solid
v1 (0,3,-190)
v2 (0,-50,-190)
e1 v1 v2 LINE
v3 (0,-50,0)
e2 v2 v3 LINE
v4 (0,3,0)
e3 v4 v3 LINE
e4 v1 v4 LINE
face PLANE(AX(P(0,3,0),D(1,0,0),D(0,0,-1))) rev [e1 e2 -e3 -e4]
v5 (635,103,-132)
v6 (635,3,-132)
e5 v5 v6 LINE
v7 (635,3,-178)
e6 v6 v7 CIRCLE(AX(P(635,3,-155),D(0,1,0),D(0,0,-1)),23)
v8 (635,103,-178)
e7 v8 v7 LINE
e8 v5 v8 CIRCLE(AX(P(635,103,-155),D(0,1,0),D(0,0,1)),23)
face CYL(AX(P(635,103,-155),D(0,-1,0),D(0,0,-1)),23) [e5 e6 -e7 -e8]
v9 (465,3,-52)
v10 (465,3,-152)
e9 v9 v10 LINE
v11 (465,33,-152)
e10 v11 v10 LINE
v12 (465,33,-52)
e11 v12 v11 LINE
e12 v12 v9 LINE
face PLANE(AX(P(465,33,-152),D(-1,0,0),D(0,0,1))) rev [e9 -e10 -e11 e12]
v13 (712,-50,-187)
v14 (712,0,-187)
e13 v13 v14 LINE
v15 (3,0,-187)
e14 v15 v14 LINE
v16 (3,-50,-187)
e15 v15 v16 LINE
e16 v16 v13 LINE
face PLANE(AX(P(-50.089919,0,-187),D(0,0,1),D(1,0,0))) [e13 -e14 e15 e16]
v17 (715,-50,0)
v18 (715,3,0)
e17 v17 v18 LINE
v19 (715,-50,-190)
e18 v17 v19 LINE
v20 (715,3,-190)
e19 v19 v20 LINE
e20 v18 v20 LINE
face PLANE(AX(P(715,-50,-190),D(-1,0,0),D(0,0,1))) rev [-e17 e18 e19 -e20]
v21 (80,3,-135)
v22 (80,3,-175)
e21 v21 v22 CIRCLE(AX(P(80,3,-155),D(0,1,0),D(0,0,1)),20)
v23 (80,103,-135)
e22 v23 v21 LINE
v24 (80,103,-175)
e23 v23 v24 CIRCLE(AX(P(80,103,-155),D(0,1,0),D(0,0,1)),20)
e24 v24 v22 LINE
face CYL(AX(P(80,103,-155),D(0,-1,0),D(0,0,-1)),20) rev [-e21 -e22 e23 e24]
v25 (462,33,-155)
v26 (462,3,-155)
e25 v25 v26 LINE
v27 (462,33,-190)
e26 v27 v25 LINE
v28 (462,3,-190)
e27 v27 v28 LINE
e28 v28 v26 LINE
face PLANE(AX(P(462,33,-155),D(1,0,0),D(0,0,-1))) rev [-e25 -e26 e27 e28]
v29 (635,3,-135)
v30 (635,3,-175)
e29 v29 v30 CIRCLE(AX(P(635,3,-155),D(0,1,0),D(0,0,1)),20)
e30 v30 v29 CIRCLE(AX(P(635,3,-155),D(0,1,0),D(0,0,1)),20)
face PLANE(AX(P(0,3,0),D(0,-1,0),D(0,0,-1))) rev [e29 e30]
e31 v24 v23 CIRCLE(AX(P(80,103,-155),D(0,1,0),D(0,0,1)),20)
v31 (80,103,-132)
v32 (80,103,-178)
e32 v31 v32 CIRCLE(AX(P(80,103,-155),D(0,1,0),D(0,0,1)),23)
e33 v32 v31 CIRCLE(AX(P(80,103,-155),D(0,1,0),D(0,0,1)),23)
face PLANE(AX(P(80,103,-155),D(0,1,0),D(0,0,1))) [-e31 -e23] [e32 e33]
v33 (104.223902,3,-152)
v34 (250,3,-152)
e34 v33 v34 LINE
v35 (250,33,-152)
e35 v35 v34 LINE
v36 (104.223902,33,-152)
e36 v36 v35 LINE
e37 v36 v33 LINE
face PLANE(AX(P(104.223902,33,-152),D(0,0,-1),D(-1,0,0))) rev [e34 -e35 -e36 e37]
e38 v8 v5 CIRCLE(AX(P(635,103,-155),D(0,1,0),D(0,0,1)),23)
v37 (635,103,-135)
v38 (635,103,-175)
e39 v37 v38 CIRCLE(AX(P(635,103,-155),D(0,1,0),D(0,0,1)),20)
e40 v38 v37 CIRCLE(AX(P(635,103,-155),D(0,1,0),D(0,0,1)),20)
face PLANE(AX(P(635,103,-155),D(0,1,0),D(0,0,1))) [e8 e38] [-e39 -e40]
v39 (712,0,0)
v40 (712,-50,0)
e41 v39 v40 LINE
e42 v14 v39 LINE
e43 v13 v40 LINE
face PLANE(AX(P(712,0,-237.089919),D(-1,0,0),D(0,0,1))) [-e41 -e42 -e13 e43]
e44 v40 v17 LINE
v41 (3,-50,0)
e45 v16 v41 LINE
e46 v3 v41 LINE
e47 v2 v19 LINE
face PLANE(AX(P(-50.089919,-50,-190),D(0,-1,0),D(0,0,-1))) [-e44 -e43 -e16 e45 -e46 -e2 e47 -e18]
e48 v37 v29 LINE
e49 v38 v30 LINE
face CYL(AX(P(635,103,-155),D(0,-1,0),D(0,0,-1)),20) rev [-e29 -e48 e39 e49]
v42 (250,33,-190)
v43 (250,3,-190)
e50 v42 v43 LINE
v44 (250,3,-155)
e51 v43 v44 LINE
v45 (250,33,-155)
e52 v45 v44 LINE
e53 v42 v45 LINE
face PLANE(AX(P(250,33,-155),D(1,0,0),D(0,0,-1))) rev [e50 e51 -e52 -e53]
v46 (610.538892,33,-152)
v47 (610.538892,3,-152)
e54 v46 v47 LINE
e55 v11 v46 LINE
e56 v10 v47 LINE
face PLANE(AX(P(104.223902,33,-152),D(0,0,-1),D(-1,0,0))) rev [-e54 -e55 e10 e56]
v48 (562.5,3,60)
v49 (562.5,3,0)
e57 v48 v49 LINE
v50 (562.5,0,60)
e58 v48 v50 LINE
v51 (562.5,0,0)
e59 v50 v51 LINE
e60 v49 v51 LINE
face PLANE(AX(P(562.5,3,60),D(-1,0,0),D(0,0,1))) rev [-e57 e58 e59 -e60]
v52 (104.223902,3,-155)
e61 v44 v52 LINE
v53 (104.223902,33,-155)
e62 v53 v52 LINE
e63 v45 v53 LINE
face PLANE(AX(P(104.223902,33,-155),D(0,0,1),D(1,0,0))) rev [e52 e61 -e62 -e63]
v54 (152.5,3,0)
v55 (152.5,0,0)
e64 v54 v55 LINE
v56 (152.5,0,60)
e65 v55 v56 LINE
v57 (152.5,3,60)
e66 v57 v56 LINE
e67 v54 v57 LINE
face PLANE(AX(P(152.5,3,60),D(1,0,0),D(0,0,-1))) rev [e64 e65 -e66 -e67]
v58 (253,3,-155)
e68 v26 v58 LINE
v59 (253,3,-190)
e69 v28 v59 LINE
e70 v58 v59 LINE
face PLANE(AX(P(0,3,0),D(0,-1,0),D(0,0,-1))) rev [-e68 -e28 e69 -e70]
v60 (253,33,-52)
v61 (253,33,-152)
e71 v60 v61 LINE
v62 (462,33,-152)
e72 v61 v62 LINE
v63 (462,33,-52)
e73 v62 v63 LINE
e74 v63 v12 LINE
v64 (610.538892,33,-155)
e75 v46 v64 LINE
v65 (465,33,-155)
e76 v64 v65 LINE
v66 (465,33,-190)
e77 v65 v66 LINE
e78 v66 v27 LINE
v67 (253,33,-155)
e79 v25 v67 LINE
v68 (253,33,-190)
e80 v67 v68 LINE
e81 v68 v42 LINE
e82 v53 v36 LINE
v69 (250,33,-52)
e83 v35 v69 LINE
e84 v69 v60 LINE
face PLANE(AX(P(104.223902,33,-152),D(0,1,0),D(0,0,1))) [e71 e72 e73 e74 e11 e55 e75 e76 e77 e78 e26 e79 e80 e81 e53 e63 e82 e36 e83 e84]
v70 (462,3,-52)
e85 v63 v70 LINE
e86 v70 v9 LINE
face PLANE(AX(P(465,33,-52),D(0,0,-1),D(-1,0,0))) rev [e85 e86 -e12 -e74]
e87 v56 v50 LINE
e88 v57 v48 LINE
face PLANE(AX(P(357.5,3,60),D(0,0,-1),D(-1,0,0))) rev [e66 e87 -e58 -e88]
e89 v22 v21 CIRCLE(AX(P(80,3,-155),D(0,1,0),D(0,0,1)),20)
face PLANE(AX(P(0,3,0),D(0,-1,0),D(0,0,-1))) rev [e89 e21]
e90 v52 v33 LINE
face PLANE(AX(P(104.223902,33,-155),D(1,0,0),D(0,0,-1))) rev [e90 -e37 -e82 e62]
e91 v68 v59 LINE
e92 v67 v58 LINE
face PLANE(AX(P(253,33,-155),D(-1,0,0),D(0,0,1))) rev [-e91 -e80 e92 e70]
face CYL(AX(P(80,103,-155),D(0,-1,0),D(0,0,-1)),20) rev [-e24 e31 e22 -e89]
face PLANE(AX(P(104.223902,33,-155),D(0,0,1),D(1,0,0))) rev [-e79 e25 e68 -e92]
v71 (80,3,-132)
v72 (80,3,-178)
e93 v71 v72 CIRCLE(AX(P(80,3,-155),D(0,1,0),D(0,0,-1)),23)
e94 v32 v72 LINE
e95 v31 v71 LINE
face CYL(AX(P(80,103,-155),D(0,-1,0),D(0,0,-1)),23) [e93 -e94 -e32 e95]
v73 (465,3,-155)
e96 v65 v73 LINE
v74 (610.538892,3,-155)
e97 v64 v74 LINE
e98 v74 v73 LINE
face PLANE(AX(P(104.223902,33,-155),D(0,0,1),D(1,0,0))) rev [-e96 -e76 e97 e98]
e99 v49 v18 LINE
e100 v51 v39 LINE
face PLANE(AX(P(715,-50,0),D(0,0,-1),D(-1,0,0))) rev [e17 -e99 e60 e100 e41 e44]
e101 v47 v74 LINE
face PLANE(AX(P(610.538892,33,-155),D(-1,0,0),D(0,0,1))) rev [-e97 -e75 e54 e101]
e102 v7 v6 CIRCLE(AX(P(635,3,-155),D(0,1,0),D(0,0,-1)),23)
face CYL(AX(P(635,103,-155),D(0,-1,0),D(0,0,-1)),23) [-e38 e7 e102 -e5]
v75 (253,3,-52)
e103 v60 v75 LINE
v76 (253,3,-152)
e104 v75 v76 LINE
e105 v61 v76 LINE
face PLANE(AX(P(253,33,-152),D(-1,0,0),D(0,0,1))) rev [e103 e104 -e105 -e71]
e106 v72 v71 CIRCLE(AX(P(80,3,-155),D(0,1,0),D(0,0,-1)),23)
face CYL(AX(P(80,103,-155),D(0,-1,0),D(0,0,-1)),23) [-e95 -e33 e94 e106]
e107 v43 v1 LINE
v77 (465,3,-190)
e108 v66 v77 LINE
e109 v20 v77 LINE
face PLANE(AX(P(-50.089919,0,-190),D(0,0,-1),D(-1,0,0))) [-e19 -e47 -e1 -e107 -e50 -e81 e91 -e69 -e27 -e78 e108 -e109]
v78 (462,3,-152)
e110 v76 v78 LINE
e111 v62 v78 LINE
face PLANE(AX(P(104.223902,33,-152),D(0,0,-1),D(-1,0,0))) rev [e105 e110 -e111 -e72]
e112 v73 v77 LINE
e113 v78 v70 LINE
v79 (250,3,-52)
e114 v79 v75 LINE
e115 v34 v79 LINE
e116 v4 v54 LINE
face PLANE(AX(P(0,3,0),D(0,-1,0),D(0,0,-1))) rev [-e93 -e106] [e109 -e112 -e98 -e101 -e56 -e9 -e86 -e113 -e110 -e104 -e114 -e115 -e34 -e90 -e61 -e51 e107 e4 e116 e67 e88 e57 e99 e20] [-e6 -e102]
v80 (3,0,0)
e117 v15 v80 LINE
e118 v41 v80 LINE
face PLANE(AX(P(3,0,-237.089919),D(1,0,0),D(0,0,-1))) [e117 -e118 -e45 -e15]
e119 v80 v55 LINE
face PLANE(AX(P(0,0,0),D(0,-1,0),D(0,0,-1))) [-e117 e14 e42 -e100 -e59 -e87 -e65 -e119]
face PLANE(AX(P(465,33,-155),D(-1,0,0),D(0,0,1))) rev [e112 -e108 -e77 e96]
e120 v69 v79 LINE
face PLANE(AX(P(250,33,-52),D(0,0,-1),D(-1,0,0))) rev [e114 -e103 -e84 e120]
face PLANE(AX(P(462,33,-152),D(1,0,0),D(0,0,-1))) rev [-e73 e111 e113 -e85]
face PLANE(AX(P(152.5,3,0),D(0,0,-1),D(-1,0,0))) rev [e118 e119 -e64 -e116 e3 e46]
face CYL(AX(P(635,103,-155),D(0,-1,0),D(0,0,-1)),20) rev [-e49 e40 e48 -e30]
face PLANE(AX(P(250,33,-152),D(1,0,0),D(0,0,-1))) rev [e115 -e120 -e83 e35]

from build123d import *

# Parameters (mm, degrees)
EXTRUDE_1_DEPTH  = 3
SKETCH_2_R       = 23
SKETCH_2_R_2     = 20
EXTRUDE_2_DEPTH  = 100
SKETCH_4_W       = 3
SKETCH_4_H       = 50
EXTRUDE_3_DEPTH  = 715
SKETCH_7_W       = 506.314990664
SKETCH_7_H       = 3
EXTRUDE_8_DEPTH  = 30
SKETCH_8_W       = 3
SKETCH_8_H       = 35
SKETCH_8_H_2     = 100
EXTRUDE_9_DEPTH  = 30
SKETCH_9_W       = 3
SKETCH_9_H       = 50
EXTRUDE_10_DEPTH = 187


with BuildPart() as part:
    # 草图1 → 凸台-拉伸1 (new body)
    with BuildSketch(Plane(origin=(0, 0, 0), x_dir=(1, 0, 0), z_dir=(0, 1, 0))):
        Polygon((357.5, -60), (152.5, -60), (152.5, 0), (0, 0), (0, 190), (715, 190), (715, 0), (562.5, 0), (562.5, -60), align=None)
    extrude(amount=EXTRUDE_1_DEPTH)

    # 草图2 → 凸台-拉伸2 (add)
    # profile 1 of 2: a face of its own
    with BuildSketch(Plane(origin=(0, 3, 0), x_dir=(1, 0, 0), z_dir=(0, 1, 0))):
        with Locations(Location((80, 155, 0), (0, 0, 90))):
            Circle(SKETCH_2_R)
        with Locations(Location((80, 155, 0), (0, 0, 270))):
            Circle(SKETCH_2_R_2, mode=Mode.SUBTRACT)
    # profile 2 of 2: a face of its own
    with BuildSketch(Plane(origin=(0, 3, 0), x_dir=(1, 0, 0), z_dir=(0, 1, 0))):
        with Locations(Location((635, 155, 0), (0, 0, 90))):
            Circle(SKETCH_2_R)
        with Locations(Location((635, 155, 0), (0, 0, 270))):
            Circle(SKETCH_2_R_2, mode=Mode.SUBTRACT)
    extrude(amount=EXTRUDE_2_DEPTH)

    # 草图7 → 凸台-拉伸8 (add)
    with BuildSketch(Plane(origin=(0, 3, 0), x_dir=(1, 0, 0), z_dir=(0, 1, 0))):
        with Locations((357.381396842, 153.5)):
            Rectangle(SKETCH_7_W, SKETCH_7_H)
    extrude(amount=EXTRUDE_8_DEPTH)

    # 草图8 → 凸台-拉伸9 (add)
    with BuildSketch(Plane(origin=(0, 3, 0), x_dir=(1, 0, 0), z_dir=(0, 1, 0))):
        with Locations((251.5, 172.5)):
            Rectangle(SKETCH_8_W, SKETCH_8_H)
        with Locations((251.5, 102)):
            Rectangle(SKETCH_8_W, SKETCH_8_H_2)
        with Locations((463.5, 102)):
            Rectangle(SKETCH_8_W, SKETCH_8_H_2)
        with Locations((463.5, 172.5)):
            Rectangle(SKETCH_8_W, SKETCH_8_H)
    extrude(amount=EXTRUDE_9_DEPTH)



with BuildPart() as body_2:
    # 草图4 → 凸台-拉伸3 (new body)
    with BuildSketch(Plane(origin=(715, 0, 0), x_dir=(0, 0, -1), z_dir=(1, 0, 0))):
        with Locations((188.5, -25)):
            Rectangle(SKETCH_4_W, SKETCH_4_H)
    extrude(amount=-EXTRUDE_3_DEPTH)


with BuildPart() as part_1:
    add(part.part)

    add(body_2.part)  # 凸台-拉伸10 merges body 2
    # 草图9 → 凸台-拉伸10 (add)
    with BuildSketch(Plane.XY):
        with Locations((713.5, -25)):
            Rectangle(SKETCH_9_W, SKETCH_9_H)
        with Locations((1.5, -25)):
            Rectangle(SKETCH_9_W, SKETCH_9_H)
    extrude(amount=-EXTRUDE_10_DEPTH)


solid = part_1.part
